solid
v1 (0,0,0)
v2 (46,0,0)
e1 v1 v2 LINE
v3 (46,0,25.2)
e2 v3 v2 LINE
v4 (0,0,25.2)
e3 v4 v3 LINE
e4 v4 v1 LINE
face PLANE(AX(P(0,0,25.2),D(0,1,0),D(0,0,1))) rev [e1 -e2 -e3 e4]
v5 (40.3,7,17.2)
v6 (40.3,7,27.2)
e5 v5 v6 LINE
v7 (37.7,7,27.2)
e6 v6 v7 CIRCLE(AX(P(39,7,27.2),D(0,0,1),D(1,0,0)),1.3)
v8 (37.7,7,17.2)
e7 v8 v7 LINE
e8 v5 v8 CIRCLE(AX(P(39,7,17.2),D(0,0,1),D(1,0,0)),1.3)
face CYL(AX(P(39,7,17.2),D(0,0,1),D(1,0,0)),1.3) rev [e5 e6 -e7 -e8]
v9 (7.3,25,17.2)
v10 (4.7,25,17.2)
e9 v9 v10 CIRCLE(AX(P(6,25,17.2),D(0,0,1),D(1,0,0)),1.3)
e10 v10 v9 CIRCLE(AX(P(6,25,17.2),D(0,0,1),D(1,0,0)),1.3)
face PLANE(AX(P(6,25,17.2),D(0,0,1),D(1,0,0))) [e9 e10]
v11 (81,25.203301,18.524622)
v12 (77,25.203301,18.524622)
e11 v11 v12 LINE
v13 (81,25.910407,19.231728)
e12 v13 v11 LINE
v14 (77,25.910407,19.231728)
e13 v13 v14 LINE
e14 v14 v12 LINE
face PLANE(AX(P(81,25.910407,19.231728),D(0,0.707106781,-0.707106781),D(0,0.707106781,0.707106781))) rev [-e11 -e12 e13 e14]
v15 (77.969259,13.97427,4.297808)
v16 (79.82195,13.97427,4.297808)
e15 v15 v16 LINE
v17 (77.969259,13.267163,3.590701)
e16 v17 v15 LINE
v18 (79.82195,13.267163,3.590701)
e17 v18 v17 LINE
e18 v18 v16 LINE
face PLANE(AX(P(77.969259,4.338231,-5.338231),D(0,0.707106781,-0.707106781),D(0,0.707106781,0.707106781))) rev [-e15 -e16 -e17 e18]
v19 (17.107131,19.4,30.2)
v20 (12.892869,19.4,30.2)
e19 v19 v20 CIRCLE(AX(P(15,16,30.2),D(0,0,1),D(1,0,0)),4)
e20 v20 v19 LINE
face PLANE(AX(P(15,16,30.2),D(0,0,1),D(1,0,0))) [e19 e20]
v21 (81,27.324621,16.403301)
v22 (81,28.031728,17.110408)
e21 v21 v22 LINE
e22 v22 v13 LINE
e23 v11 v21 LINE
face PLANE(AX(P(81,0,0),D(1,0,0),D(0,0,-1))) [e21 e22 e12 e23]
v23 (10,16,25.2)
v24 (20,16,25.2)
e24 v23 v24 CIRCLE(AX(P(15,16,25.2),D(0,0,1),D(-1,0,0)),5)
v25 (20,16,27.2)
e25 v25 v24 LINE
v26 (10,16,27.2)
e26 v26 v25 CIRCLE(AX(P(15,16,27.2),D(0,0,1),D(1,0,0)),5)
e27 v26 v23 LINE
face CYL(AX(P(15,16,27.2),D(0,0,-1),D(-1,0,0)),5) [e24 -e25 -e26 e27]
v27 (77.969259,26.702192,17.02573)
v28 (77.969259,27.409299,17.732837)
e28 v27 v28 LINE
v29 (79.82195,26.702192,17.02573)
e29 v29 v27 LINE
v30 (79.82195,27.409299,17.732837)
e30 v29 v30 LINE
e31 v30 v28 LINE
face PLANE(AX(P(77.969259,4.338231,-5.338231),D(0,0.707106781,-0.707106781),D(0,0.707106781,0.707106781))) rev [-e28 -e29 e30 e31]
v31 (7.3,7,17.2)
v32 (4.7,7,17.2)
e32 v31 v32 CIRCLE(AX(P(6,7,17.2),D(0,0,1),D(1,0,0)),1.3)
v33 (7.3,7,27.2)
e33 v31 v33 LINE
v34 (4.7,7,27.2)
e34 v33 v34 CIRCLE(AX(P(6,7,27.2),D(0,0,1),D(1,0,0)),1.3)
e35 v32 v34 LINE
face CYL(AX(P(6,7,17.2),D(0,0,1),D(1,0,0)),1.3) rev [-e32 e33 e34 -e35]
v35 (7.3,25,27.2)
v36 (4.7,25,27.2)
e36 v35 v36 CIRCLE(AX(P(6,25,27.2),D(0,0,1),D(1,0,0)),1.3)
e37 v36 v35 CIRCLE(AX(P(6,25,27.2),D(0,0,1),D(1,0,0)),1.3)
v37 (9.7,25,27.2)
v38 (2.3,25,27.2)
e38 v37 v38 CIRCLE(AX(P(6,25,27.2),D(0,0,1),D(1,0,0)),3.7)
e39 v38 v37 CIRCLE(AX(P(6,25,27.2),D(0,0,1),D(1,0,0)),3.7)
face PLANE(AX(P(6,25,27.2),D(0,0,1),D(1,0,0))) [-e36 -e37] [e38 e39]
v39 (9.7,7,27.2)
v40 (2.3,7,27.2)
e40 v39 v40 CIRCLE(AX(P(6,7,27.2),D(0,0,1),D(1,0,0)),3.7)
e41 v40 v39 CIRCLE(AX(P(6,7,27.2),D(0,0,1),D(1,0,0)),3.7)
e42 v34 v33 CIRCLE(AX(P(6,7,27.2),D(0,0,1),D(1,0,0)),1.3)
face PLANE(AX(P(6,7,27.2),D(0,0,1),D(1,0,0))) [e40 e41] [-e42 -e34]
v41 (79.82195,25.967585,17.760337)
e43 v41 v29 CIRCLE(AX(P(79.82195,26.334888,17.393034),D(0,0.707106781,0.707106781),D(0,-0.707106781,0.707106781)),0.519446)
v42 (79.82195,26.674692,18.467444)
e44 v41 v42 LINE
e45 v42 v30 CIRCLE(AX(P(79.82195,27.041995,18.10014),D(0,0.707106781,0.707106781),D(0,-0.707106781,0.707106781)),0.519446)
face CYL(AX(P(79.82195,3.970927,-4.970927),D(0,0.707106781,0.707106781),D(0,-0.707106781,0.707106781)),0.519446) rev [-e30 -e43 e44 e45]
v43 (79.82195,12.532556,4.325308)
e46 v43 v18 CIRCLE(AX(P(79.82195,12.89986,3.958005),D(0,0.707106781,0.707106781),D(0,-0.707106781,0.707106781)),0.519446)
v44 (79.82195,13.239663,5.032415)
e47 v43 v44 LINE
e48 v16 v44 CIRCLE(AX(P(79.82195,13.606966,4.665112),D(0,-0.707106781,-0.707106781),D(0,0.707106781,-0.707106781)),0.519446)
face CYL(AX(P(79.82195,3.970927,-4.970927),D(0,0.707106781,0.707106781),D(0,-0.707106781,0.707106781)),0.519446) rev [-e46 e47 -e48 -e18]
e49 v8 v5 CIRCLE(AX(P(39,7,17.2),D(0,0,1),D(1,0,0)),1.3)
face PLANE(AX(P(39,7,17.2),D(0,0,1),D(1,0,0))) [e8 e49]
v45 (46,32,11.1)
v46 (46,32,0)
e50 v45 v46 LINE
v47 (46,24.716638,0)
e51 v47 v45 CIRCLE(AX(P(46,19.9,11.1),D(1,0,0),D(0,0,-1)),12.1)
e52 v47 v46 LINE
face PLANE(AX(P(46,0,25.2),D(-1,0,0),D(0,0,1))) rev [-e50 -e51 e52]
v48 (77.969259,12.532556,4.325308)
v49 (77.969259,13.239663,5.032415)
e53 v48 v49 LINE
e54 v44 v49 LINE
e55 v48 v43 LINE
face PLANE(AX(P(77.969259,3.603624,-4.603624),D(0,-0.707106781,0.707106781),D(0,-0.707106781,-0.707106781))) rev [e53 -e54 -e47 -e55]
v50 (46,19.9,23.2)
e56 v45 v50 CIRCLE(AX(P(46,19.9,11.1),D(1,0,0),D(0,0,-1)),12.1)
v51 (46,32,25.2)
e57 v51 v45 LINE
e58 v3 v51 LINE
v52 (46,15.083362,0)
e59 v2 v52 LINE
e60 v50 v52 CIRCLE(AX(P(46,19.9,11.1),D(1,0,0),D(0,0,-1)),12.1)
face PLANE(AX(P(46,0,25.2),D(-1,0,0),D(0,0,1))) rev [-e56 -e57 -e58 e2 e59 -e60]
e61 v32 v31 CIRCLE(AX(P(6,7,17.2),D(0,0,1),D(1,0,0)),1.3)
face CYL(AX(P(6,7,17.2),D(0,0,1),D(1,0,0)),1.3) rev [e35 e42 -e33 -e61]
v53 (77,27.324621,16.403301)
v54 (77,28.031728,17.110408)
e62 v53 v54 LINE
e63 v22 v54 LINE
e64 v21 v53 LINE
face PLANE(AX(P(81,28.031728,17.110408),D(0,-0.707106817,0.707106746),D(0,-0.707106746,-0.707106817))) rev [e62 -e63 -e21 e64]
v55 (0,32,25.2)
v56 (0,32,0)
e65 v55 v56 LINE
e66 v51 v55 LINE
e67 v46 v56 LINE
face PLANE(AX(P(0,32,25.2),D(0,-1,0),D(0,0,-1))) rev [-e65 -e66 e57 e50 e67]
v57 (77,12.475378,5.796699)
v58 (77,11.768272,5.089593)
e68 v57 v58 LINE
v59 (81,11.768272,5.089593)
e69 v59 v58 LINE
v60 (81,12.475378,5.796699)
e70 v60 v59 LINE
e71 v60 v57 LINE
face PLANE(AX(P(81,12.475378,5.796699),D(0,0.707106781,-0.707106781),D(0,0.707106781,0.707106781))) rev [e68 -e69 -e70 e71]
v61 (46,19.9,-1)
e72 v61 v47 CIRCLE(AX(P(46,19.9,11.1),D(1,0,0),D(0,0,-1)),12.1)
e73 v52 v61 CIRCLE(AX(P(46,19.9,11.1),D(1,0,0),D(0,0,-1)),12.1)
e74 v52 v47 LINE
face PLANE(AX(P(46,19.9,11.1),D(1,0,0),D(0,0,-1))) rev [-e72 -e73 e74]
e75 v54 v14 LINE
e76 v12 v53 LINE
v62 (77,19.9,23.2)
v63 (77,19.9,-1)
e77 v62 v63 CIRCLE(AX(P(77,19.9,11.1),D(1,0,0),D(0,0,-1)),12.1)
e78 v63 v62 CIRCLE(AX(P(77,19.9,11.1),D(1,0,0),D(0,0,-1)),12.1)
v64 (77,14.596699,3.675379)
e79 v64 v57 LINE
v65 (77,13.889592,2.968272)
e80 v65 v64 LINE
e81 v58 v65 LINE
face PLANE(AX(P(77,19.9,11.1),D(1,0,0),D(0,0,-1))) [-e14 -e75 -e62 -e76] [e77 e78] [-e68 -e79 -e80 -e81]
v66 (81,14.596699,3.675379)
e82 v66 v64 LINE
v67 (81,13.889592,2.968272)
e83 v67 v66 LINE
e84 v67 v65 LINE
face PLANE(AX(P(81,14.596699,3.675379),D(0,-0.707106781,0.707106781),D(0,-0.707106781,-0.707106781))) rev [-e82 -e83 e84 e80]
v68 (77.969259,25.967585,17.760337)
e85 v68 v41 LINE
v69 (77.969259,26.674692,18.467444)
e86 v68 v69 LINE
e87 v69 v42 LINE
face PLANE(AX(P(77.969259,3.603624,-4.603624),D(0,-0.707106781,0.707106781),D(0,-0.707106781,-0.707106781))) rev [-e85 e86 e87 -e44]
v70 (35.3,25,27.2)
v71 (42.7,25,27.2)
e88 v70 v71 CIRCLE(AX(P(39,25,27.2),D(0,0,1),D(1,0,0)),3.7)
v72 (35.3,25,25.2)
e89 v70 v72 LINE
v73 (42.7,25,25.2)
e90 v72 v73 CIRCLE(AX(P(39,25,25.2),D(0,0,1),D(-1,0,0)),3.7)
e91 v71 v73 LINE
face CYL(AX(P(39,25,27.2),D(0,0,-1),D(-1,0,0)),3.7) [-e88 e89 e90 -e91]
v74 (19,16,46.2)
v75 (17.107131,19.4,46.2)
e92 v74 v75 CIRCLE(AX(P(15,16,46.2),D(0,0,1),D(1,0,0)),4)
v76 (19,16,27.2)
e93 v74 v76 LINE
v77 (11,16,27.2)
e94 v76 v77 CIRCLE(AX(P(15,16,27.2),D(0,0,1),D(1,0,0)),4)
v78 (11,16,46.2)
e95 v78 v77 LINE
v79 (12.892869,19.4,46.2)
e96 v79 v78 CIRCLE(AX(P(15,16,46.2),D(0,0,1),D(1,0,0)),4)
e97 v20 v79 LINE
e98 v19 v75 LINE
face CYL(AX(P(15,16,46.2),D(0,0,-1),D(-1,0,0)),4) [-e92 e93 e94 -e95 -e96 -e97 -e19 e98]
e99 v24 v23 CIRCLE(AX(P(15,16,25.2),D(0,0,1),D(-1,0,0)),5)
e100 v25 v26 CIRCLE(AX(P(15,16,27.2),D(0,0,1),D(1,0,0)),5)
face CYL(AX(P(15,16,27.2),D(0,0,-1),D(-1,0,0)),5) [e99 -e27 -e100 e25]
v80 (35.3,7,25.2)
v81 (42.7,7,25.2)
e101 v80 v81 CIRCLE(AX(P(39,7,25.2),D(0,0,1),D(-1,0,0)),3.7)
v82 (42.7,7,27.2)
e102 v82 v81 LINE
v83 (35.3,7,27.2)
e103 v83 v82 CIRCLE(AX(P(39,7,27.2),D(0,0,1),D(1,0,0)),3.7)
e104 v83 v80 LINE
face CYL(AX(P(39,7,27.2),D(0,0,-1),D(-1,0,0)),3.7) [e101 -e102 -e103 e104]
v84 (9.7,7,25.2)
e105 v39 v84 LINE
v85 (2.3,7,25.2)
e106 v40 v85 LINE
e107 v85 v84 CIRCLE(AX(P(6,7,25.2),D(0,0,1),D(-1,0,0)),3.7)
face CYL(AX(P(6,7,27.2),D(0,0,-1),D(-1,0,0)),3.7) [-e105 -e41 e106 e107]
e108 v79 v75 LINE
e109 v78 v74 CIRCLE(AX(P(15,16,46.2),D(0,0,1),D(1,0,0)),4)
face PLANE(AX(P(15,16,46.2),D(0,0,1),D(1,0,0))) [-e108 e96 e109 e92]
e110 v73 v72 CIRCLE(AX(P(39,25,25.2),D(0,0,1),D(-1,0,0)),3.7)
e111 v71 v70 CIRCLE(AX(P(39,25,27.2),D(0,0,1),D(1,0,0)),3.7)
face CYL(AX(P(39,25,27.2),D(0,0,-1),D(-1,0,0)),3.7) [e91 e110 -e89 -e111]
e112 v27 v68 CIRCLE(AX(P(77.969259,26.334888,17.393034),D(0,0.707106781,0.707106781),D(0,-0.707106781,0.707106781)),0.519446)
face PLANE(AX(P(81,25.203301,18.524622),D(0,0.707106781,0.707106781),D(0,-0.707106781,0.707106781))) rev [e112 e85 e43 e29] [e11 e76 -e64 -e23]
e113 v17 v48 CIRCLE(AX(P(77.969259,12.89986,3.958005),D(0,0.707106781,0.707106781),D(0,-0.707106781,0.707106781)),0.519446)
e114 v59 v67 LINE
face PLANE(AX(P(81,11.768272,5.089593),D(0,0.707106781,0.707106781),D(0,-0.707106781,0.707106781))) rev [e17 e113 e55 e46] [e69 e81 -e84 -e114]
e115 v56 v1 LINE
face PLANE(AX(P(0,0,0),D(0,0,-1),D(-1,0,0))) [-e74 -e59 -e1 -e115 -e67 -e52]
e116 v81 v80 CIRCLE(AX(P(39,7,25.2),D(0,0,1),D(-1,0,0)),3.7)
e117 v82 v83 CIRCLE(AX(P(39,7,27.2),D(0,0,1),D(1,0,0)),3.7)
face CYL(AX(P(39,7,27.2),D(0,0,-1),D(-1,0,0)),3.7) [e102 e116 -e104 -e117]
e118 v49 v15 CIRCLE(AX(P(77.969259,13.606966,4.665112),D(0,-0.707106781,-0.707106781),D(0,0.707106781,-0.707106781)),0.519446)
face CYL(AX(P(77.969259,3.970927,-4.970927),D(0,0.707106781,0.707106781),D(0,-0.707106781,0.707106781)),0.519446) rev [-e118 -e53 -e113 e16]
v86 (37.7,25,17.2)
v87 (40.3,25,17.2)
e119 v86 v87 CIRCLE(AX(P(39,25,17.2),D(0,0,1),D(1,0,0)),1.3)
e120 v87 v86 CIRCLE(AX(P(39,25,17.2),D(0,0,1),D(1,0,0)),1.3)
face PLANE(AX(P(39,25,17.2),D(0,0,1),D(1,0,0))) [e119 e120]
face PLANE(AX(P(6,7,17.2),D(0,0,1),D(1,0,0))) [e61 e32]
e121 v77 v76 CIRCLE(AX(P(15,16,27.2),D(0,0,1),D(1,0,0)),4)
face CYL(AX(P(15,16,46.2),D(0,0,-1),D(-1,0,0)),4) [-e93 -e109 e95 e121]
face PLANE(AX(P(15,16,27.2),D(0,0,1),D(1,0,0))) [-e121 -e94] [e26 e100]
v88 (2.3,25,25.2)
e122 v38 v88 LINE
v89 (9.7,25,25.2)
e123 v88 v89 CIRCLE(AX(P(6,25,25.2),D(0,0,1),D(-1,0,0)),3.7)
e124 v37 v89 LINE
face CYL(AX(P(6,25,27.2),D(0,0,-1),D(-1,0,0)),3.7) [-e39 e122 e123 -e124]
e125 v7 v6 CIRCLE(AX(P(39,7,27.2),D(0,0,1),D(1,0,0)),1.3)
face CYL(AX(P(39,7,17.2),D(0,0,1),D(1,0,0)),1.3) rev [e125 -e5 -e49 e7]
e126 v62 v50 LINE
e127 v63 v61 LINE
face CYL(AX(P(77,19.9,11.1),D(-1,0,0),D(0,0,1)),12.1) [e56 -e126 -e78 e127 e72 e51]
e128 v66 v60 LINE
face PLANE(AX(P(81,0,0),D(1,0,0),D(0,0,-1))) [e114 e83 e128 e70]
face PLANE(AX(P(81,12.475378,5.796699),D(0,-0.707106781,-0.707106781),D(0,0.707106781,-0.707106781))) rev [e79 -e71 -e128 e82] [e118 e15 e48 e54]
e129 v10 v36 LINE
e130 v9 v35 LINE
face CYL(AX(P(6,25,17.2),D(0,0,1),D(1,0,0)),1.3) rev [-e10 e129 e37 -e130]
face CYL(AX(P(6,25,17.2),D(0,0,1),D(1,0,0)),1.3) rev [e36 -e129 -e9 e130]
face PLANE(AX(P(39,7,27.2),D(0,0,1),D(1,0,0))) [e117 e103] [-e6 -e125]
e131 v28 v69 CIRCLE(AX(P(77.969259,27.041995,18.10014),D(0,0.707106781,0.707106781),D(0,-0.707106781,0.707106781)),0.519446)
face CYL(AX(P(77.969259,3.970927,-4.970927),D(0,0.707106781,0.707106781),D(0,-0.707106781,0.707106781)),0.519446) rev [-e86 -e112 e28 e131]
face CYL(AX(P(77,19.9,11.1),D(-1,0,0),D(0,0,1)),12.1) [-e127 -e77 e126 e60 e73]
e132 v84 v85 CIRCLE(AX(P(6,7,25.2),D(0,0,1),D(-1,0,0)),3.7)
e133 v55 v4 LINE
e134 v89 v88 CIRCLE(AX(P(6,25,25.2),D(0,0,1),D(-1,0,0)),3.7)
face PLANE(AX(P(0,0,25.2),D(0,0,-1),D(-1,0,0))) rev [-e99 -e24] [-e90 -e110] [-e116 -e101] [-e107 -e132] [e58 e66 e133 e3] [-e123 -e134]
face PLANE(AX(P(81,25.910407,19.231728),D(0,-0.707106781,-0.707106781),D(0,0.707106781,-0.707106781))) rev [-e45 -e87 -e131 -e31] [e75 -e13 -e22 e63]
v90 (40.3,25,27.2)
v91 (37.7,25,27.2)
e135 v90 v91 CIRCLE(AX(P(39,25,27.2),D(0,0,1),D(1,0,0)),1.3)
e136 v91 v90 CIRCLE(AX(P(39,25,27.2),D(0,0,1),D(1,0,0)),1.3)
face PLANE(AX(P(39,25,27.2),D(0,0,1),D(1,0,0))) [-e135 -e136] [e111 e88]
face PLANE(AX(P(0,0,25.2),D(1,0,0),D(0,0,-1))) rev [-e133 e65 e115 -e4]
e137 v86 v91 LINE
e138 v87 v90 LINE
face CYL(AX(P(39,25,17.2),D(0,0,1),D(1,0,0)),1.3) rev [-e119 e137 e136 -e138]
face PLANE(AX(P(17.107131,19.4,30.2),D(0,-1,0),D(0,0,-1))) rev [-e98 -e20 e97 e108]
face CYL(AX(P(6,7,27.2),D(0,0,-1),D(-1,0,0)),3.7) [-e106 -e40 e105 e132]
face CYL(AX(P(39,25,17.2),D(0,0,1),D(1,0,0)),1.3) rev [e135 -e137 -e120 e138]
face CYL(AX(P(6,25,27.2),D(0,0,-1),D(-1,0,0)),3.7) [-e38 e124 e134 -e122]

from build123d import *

# Parameters (mm, degrees)
SKETCH_1_W          = 46
SKETCH_1_H          = 32
EXTRUDE_1_DEPTH     = 25.2
SKETCH_2_R          = 3.7
SKETCH_2_R_2        = 5
EXTRUDE_2_DEPTH     = 2
SKETCH_3_R          = 1.3
CUT_EXTRUDE_1_DEPTH = 10
SKETCH_4_R          = 4
EXTRUDE_3_DEPTH     = 19
CUT_EXTRUDE_START   = -16
CUT_EXTRUDE_2_DEPTH = 16
SKETCH_6_R          = 12.1
EXTRUDE_4_DEPTH     = 31
EXTRUDE_5_DEPTH     = 4
CUT_EXTRUDE_3_DEPTH = 88.342884876


with BuildPart() as part:
    # 草图1 → 凸台-拉伸1 (new body)
    with BuildSketch(Plane.XY):
        with Locations((23, 16)):
            Rectangle(SKETCH_1_W, SKETCH_1_H)
    extrude(amount=EXTRUDE_1_DEPTH)

    # 草图2 → 凸台-拉伸2 (add)
    with BuildSketch(Plane.XY.offset(25.2)):
        with Locations(Location((6, 25, 0), (0, 0, 180))):
            Circle(SKETCH_2_R)
        with Locations(Location((6, 7, 0), (0, 0, 180))):
            Circle(SKETCH_2_R)
        with Locations(Location((39, 7, 0), (0, 0, 180))):
            Circle(SKETCH_2_R)
        with Locations(Location((39, 25, 0), (0, 0, 180))):
            Circle(SKETCH_2_R)
        with Locations(Location((15, 16, 0), (0, 0, 180))):
            Circle(SKETCH_2_R_2)
    extrude(amount=EXTRUDE_2_DEPTH)

    # 草图3 → 切除-拉伸1 (cut)
    with BuildSketch(Plane.XY.offset(27.2)):
        with Locations((6, 7)):
            Circle(SKETCH_3_R)
        with Locations((6, 25)):
            Circle(SKETCH_3_R)
        with Locations((39, 25)):
            Circle(SKETCH_3_R)
        with Locations((39, 7)):
            Circle(SKETCH_3_R)
    extrude(amount=-CUT_EXTRUDE_1_DEPTH, mode=Mode.SUBTRACT)

    # 草图4 → 凸台-拉伸3 (add)
    with BuildSketch(Plane.XY.offset(27.2)):
        with Locations((15, 16)):
            Circle(SKETCH_4_R)
    extrude(amount=EXTRUDE_3_DEPTH)

    # 草图5 → 切除-拉伸2 (cut)
    with BuildSketch(Plane.XY.offset(46.2).offset(CUT_EXTRUDE_START)):
        with BuildLine():
            Line((17.107130751, 19.4), (12.892869249, 19.4))
            ThreePointArc((12.892869249, 19.4), (15, 20), (17.107130751, 19.4))
        make_face()
    extrude(amount=CUT_EXTRUDE_2_DEPTH, mode=Mode.SUBTRACT)

    # 草图6 → 凸台-拉伸4 (add)
    with BuildSketch(Plane(origin=(46, 0, 0), x_dir=(0, 0, -1), z_dir=(1, 0, 0))):
        with Locations(Location((-11.1, 19.9, 0), (0, 0, 90))):
            Circle(SKETCH_6_R)
    extrude(amount=EXTRUDE_4_DEPTH)

    # 草图7 → 凸台-拉伸5 (add)
    with BuildSketch(Plane(origin=(77, 0, 0), x_dir=(0, 0, -1), z_dir=(1, 0, 0))):
        Polygon((-19.231728338, 25.910407286), (-17.110407994, 28.03172763), (-16.403301178, 27.324620884), (-18.524621557, 25.203300505), align=None)
        Polygon((-5.796699495, 12.475378443), (-3.675379152, 14.596698787), (-2.96827237, 13.889592006), (-5.089592714, 11.768271662), align=None)
    extrude(amount=EXTRUDE_5_DEPTH)

    # 草图8 → 切除-拉伸3 (cut, through all)
    with BuildSketch(Plane(origin=(0, 22.571067812, 22.571067812), x_dir=(1, 0, 0), z_dir=(0, 0.7071067811865464, 0.7071067811865487))):
        with BuildLine():
            Line((77.969259397, 6.842291957), (79.821949512, 6.842291957))
            ThreePointArc((79.821949512, 6.842291957), (80.341395338, 6.32284613), (79.821949512, 5.803400304))
            Line((79.821949512, 5.803400304), (77.969259397, 5.803400304))
            ThreePointArc((77.969259397, 5.803400304), (77.44981357, 6.32284613), (77.969259397, 6.842291957))
        make_face()
    extrude(amount=-CUT_EXTRUDE_3_DEPTH, mode=Mode.SUBTRACT)


solid = part.part
